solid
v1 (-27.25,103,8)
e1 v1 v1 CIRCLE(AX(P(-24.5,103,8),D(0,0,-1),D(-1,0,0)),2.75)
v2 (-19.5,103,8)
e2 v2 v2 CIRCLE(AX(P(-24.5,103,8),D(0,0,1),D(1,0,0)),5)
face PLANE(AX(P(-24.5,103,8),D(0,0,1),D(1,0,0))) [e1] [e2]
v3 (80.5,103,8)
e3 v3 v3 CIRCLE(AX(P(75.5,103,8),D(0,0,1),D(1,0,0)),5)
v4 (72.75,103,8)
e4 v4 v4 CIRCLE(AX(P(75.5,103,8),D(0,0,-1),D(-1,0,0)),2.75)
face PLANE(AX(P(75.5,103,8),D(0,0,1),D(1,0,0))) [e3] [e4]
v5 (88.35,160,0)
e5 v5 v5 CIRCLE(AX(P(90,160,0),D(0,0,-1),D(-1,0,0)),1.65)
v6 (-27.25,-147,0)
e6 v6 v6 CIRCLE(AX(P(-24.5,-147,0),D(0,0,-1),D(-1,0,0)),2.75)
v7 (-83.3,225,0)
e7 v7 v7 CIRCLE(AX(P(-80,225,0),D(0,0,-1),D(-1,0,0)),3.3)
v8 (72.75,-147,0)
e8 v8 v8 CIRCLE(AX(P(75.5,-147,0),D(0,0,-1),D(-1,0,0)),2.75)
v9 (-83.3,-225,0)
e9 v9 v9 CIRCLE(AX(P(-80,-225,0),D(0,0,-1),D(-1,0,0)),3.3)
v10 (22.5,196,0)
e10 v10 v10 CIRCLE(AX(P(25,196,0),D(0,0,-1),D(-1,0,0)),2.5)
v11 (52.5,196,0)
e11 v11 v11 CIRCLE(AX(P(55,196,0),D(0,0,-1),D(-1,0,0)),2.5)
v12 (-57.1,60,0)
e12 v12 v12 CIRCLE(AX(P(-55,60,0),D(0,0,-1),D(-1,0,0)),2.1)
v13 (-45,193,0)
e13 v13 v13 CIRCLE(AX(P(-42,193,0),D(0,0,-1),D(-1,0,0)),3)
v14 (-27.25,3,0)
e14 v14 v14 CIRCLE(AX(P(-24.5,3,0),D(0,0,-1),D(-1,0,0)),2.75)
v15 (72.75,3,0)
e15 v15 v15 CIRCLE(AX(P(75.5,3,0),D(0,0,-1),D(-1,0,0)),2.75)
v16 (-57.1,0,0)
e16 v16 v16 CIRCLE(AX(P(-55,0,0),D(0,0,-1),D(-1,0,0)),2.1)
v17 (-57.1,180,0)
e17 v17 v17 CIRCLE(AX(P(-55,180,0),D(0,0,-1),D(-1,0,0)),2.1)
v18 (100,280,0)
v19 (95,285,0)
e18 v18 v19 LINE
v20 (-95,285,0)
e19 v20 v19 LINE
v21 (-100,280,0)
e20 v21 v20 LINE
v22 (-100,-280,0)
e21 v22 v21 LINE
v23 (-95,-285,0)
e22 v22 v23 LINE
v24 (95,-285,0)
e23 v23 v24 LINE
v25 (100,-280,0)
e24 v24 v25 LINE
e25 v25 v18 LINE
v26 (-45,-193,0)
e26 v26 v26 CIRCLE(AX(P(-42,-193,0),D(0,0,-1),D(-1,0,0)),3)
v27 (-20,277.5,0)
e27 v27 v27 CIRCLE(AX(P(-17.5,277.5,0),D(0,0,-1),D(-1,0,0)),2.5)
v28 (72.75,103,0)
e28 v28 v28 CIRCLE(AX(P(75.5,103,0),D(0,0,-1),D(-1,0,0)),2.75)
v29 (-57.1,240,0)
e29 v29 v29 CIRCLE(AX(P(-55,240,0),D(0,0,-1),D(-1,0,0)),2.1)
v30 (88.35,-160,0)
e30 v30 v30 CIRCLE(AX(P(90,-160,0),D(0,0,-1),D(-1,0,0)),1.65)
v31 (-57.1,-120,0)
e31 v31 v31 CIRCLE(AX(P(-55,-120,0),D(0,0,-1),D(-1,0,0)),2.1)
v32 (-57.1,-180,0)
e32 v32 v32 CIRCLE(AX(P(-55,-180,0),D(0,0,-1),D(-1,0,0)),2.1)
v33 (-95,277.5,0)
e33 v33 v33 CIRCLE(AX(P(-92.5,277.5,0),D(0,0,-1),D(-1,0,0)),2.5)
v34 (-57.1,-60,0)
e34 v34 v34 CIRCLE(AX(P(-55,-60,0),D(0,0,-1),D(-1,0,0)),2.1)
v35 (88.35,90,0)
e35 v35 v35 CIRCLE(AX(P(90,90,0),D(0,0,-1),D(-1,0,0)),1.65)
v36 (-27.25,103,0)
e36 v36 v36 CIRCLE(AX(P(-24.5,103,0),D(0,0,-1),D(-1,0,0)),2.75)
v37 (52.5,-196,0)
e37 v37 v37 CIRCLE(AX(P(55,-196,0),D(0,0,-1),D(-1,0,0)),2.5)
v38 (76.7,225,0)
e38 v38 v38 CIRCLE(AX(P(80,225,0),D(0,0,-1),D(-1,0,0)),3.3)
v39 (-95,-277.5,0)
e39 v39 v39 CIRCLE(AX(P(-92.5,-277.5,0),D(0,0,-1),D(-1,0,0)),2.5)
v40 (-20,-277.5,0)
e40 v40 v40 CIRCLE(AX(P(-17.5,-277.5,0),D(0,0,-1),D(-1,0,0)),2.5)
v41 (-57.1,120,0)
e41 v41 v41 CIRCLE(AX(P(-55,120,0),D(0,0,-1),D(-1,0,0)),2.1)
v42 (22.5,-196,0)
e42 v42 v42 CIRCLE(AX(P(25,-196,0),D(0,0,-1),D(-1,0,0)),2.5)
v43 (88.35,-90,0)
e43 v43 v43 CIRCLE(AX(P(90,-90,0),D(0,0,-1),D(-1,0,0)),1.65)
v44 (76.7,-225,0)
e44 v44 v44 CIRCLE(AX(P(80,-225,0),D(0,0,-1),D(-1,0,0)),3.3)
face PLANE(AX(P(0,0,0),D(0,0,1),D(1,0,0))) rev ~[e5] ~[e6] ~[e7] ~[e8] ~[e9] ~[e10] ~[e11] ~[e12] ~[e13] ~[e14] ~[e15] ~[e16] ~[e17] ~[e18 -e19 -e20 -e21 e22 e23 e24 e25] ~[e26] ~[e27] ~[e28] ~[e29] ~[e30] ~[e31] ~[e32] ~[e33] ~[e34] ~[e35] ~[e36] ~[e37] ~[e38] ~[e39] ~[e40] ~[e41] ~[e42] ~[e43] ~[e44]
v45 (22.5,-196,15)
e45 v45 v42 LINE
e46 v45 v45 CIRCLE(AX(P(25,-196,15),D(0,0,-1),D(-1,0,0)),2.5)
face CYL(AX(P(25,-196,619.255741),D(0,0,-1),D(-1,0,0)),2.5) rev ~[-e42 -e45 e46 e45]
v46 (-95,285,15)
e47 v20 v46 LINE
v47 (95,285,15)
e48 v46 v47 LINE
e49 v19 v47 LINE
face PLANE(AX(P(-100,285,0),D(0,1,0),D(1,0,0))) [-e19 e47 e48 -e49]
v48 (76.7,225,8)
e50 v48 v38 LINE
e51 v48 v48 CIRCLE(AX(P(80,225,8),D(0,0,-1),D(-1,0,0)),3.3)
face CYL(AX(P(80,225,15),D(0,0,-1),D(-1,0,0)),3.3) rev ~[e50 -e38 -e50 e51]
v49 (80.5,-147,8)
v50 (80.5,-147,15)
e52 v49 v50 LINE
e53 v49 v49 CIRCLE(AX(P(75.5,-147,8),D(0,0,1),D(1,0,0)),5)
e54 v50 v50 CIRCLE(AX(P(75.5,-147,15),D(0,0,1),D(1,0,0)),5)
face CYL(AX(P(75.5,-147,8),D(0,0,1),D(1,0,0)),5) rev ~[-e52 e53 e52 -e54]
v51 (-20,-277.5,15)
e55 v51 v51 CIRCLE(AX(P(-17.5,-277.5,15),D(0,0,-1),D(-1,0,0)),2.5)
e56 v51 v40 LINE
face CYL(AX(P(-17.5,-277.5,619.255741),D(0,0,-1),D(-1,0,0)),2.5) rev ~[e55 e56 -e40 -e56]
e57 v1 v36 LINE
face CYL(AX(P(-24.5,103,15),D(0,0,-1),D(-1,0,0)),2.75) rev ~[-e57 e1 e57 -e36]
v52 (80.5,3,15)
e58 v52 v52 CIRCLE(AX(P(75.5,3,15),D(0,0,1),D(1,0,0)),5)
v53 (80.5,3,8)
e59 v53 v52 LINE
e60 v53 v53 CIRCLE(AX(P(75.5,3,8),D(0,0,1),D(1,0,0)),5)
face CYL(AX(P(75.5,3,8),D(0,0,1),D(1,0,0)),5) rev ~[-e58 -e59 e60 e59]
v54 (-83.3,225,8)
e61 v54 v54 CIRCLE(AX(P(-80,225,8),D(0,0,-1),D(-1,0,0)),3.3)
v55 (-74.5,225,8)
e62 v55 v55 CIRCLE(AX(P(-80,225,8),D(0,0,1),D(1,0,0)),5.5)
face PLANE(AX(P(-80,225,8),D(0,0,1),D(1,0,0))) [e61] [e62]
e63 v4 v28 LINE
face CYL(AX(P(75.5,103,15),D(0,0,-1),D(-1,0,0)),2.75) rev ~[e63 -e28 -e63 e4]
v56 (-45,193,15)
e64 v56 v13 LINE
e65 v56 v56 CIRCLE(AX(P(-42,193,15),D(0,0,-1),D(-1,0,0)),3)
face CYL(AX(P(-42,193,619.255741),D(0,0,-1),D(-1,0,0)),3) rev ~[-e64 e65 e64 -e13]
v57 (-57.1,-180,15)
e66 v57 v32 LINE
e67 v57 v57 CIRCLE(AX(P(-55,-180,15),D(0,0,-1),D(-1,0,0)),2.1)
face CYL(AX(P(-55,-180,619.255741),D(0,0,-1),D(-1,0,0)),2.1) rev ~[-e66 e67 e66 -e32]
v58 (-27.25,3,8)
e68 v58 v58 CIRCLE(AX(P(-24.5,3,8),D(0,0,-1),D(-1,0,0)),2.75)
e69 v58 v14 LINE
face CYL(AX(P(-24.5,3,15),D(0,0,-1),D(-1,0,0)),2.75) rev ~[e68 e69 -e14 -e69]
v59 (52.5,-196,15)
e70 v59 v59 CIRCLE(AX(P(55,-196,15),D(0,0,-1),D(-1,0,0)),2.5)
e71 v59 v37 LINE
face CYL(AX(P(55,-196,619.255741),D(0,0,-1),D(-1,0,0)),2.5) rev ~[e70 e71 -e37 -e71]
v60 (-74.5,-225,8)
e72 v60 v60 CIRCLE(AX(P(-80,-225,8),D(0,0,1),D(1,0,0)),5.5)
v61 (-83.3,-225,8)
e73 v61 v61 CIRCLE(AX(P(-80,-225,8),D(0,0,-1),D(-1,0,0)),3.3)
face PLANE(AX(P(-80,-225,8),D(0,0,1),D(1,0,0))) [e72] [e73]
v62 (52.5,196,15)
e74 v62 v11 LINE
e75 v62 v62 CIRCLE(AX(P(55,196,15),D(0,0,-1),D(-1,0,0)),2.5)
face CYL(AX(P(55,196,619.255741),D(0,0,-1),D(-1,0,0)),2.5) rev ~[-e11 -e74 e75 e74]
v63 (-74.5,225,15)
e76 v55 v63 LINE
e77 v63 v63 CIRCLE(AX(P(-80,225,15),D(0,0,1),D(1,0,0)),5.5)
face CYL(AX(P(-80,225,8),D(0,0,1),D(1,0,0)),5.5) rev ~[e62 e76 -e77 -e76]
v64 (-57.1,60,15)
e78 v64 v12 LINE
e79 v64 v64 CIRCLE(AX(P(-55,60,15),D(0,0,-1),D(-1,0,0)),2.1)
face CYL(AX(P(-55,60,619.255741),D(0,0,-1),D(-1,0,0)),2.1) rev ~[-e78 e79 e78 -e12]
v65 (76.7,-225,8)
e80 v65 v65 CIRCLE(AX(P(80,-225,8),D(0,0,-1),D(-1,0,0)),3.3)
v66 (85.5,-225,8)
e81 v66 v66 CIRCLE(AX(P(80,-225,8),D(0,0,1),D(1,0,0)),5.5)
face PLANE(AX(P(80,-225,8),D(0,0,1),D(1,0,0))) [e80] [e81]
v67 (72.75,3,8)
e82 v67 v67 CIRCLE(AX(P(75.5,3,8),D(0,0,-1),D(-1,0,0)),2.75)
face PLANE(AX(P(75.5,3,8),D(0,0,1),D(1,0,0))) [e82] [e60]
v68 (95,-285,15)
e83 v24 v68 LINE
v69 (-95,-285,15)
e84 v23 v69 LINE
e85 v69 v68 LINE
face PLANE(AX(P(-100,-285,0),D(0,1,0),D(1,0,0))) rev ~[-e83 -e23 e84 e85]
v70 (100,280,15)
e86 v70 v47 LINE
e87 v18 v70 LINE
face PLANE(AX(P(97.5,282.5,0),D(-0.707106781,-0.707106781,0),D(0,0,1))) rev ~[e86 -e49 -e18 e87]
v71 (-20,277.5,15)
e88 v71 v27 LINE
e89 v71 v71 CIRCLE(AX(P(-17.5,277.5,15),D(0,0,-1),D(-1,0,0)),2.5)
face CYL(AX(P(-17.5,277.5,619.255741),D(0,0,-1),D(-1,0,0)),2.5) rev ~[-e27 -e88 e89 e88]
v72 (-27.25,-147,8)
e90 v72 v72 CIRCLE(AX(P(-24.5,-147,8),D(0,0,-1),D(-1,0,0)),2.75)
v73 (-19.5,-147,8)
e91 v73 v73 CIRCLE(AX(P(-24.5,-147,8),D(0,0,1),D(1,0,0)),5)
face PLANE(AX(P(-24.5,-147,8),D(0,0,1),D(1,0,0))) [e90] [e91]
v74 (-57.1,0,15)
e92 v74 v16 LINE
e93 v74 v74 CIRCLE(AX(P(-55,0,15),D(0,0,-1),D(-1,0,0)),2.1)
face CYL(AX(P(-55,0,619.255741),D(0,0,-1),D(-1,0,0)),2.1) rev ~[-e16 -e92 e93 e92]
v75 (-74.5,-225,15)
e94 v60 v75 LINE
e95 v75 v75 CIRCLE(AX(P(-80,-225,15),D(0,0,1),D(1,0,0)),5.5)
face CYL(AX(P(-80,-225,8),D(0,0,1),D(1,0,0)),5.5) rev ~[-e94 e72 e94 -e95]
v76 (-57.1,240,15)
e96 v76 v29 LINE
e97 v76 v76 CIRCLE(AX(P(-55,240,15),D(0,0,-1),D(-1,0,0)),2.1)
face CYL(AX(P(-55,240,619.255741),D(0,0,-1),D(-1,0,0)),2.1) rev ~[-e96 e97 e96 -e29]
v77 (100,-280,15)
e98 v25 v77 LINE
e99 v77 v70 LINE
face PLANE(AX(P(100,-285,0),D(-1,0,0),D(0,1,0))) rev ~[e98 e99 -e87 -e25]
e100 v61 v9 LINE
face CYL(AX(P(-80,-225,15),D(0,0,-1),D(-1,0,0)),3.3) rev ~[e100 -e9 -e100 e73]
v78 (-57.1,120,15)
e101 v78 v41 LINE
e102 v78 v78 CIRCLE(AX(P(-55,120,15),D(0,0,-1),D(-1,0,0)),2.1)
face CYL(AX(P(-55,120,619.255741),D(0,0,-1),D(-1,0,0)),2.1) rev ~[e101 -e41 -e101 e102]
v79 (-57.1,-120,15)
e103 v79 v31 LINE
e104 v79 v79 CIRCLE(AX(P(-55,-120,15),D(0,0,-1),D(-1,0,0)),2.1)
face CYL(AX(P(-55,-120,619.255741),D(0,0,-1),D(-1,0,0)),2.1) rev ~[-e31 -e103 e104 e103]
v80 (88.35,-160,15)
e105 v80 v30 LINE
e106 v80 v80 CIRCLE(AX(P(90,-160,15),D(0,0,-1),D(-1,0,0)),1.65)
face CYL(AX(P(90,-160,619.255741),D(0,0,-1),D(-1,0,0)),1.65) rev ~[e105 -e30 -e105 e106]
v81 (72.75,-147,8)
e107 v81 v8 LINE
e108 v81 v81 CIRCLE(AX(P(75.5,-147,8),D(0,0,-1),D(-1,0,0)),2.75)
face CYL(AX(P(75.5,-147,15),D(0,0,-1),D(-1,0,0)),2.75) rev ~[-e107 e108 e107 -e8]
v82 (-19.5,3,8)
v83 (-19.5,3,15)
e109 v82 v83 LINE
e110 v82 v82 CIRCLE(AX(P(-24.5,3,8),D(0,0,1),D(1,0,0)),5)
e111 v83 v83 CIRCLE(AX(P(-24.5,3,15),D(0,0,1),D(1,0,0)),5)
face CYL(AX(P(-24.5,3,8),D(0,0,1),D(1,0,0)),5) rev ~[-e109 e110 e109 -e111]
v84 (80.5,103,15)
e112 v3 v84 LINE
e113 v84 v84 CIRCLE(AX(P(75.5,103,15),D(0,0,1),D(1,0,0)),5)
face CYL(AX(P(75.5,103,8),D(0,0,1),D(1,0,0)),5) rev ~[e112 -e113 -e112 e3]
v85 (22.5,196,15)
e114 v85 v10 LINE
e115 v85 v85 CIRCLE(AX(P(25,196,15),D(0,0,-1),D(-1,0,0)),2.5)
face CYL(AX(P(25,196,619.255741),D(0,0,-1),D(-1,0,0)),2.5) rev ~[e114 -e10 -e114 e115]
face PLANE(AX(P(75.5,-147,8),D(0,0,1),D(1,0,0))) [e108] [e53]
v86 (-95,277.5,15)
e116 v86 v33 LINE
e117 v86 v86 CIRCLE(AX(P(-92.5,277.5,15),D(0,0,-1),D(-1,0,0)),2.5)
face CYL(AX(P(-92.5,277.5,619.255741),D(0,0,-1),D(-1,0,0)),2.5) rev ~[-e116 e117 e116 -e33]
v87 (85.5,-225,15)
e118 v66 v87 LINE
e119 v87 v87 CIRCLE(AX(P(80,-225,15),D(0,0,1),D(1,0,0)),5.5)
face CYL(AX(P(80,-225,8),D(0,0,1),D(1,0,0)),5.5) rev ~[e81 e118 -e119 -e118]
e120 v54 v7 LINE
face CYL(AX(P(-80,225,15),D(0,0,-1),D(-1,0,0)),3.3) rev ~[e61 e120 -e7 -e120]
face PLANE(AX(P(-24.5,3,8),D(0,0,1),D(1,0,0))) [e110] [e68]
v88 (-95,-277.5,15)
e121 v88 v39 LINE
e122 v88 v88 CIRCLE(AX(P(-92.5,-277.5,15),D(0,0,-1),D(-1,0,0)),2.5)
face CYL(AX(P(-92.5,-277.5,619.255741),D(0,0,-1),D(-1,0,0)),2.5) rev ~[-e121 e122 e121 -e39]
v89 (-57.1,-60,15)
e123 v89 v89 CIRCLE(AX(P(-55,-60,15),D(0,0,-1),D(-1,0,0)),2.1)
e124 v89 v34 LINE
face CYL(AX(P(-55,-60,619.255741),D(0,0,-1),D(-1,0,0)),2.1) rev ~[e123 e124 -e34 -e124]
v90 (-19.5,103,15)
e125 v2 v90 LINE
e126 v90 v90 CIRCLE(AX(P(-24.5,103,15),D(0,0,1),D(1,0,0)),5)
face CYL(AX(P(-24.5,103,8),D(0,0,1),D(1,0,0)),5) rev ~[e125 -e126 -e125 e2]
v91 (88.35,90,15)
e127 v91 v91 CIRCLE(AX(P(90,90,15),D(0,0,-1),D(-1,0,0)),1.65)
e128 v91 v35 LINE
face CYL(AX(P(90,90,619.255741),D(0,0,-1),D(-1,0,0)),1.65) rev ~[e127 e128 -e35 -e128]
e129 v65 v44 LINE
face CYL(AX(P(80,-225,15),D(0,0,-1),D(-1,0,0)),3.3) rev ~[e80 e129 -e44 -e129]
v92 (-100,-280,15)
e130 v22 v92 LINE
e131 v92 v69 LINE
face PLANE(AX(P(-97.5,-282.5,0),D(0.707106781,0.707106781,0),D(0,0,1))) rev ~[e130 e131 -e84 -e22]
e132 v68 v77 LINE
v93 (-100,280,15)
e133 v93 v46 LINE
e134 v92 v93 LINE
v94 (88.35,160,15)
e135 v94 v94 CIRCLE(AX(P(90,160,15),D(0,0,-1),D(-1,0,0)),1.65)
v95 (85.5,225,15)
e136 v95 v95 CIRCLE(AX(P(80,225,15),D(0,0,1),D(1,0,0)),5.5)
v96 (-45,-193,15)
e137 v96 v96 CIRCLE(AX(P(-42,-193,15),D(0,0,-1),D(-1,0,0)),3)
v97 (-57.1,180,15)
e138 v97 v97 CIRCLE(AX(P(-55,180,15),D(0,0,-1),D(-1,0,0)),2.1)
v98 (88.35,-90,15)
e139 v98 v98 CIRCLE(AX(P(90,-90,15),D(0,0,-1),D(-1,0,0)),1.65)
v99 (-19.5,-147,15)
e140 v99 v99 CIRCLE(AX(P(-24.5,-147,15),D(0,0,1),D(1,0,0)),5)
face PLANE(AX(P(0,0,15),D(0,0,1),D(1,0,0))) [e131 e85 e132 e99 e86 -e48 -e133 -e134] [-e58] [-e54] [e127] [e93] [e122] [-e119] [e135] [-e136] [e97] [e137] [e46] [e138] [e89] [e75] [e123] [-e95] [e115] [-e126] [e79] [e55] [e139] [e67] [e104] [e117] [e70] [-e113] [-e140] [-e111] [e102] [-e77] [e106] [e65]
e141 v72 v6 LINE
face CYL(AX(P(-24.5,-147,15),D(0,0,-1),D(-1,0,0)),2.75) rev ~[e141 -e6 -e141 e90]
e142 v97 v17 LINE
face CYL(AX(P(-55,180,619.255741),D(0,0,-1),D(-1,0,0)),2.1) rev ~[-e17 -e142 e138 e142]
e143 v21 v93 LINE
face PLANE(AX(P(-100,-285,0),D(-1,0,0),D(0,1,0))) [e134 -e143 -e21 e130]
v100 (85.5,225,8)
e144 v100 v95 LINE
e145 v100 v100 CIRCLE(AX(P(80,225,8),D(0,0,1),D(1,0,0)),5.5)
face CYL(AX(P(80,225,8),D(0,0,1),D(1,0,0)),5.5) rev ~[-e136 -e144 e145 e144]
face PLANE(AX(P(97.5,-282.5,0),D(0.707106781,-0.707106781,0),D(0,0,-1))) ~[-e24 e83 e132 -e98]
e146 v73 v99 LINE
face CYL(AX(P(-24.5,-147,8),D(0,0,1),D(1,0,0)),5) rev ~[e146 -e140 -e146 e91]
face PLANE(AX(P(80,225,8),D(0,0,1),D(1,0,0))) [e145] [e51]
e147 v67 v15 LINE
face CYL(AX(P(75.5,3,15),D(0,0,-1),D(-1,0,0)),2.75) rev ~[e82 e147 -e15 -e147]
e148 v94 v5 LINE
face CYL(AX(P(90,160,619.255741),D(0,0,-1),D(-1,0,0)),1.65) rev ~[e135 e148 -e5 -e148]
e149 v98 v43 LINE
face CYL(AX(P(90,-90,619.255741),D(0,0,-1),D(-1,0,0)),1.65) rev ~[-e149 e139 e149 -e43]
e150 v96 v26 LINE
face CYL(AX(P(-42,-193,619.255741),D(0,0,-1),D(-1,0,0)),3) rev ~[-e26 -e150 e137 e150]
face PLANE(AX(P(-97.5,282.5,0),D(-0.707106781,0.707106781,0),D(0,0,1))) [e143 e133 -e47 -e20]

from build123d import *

# Parameters (mm, degrees)
SKETCH_1_W                   = 200
SKETCH_1_H                   = 570
EXTRUDE_1_DEPTH              = 15
CHAMFER_1_SIZE               = 5
MM_0_D                       = 6
HOLE_WIZARD_M6_1_D           = 5
HOLE_WIZARD_M5_2_D           = 4.2
HOLE_WIZARD_M6_2_D           = 5
HOLE_WIZARD_M4_1_D           = 3.3
MM_1_D                       = 1
MM_1_DEPTH                   = 17
MM_1_TIP                     = 0.30043031
HOLE_WIZARD_M5_1_D           = 5.5
HOLE_WIZARD_M5_1_DEPTH       = 17
HOLE_WIZARD_M5_1_CBORE_D     = 10
HOLE_WIZARD_M5_1_CBORE_DEPTH = 7
HOLE_WIZARD_M5_1_TIP         = 1.652366702
HOLE_WIZARD_1_D              = 6.6
HOLE_WIZARD_1_CBORE_D        = 11
HOLE_WIZARD_1_CBORE_DEPTH    = 7


with BuildPart() as part:
    # 草图1 → 凸台-拉伸1 (new body)
    with BuildSketch(Plane.XY):
        Rectangle(SKETCH_1_W, SKETCH_1_H)
    extrude(amount=EXTRUDE_1_DEPTH)

    # 倒角1
    chamfer_1_edges = [part.edges().sort_by_distance(p)[0] for p in [
        (100, -285, 7.5),
        (-100, -285, 7.5),
        (-100, 285, 7.5),
        (100, 285, 7.5),
    ]]
    chamfer(chamfer_1_edges, length=CHAMFER_1_SIZE)

    # 大小mm 暗销孔0 (through all)
    with Locations(Plane.XY.offset(15)):
        with Locations((-42, -193), (258, -193), (-42, 193), (258, 193)):
            Hole(MM_0_D / 2)

    # M6 螺纹孔1 (through all)
    with Locations(Plane.XY.offset(15)):
        with Locations((55, 196), (25, 196), (55, -196), (25, -196)):
            Hole(HOLE_WIZARD_M6_1_D / 2)

    # M5 螺纹孔2 (through all)
    with Locations(Plane.XY.offset(15)):
        with Locations((-55, 240), (-55, 180), (-55, 120), (-55, 60), (-55, 0), (-55, -60), (-55, -120), (-55, -180)):
            Hole(HOLE_WIZARD_M5_2_D / 2)

    # M6 螺纹孔2 (through all)
    with Locations(Plane.XY.offset(15)):
        with Locations((-92.500000001, -277.499999995), (-17.500000001, -277.499999995), (-17.499999995, 277.500000015), (-92.499999995, 277.500000015)):
            Hole(HOLE_WIZARD_M6_2_D / 2)

    # M4 螺纹孔1 (through all)
    with Locations(Plane.XY.offset(15)):
        with Locations((90, -160), (90, -90), (90, 90), (90, 160)):
            Hole(HOLE_WIZARD_M4_1_D / 2)

    # 大小mm 暗销孔1
    with Locations(Plane(origin=(0, 0, 0), x_dir=(-1, 0, 0), z_dir=(0, 0, -1))):
        with Locations((24.5, 103), (-75.5, 103), (24.5, -147), (-75.5, -147), (24.5, 3), (-75.5, 3)):
            Hole(MM_1_D / 2, depth=MM_1_DEPTH)
            with Locations((0, 0, -(MM_1_DEPTH + MM_1_TIP / 2))):  # 118° drill point
                Cone(0, MM_1_D / 2, MM_1_TIP, mode=Mode.SUBTRACT)

    # M5 六角凹头螺钉的柱形沉头孔1
    with Locations(Plane.XY.offset(15)):
        with Locations((75.5, -147), (75.5, 103), (75.5, 3), (-24.5, 103), (-24.5, 3), (-24.5, -147)):
            CounterBoreHole(HOLE_WIZARD_M5_1_D / 2, HOLE_WIZARD_M5_1_CBORE_D / 2, HOLE_WIZARD_M5_1_CBORE_DEPTH, depth=HOLE_WIZARD_M5_1_DEPTH)
            with Locations((0, 0, -(HOLE_WIZARD_M5_1_DEPTH + HOLE_WIZARD_M5_1_TIP / 2))):  # 118° drill point
                Cone(0, HOLE_WIZARD_M5_1_D / 2, HOLE_WIZARD_M5_1_TIP, mode=Mode.SUBTRACT)

    # 打孔尺寸(%根据)内六角花形圆柱头螺钉1 (through all)
    with Locations(Plane.XY.offset(15)):
        with Locations((-80, -225), (80, -225), (-80, 225), (80, 225)):
            CounterBoreHole(HOLE_WIZARD_1_D / 2, HOLE_WIZARD_1_CBORE_D / 2, HOLE_WIZARD_1_CBORE_DEPTH)


solid = part.part
